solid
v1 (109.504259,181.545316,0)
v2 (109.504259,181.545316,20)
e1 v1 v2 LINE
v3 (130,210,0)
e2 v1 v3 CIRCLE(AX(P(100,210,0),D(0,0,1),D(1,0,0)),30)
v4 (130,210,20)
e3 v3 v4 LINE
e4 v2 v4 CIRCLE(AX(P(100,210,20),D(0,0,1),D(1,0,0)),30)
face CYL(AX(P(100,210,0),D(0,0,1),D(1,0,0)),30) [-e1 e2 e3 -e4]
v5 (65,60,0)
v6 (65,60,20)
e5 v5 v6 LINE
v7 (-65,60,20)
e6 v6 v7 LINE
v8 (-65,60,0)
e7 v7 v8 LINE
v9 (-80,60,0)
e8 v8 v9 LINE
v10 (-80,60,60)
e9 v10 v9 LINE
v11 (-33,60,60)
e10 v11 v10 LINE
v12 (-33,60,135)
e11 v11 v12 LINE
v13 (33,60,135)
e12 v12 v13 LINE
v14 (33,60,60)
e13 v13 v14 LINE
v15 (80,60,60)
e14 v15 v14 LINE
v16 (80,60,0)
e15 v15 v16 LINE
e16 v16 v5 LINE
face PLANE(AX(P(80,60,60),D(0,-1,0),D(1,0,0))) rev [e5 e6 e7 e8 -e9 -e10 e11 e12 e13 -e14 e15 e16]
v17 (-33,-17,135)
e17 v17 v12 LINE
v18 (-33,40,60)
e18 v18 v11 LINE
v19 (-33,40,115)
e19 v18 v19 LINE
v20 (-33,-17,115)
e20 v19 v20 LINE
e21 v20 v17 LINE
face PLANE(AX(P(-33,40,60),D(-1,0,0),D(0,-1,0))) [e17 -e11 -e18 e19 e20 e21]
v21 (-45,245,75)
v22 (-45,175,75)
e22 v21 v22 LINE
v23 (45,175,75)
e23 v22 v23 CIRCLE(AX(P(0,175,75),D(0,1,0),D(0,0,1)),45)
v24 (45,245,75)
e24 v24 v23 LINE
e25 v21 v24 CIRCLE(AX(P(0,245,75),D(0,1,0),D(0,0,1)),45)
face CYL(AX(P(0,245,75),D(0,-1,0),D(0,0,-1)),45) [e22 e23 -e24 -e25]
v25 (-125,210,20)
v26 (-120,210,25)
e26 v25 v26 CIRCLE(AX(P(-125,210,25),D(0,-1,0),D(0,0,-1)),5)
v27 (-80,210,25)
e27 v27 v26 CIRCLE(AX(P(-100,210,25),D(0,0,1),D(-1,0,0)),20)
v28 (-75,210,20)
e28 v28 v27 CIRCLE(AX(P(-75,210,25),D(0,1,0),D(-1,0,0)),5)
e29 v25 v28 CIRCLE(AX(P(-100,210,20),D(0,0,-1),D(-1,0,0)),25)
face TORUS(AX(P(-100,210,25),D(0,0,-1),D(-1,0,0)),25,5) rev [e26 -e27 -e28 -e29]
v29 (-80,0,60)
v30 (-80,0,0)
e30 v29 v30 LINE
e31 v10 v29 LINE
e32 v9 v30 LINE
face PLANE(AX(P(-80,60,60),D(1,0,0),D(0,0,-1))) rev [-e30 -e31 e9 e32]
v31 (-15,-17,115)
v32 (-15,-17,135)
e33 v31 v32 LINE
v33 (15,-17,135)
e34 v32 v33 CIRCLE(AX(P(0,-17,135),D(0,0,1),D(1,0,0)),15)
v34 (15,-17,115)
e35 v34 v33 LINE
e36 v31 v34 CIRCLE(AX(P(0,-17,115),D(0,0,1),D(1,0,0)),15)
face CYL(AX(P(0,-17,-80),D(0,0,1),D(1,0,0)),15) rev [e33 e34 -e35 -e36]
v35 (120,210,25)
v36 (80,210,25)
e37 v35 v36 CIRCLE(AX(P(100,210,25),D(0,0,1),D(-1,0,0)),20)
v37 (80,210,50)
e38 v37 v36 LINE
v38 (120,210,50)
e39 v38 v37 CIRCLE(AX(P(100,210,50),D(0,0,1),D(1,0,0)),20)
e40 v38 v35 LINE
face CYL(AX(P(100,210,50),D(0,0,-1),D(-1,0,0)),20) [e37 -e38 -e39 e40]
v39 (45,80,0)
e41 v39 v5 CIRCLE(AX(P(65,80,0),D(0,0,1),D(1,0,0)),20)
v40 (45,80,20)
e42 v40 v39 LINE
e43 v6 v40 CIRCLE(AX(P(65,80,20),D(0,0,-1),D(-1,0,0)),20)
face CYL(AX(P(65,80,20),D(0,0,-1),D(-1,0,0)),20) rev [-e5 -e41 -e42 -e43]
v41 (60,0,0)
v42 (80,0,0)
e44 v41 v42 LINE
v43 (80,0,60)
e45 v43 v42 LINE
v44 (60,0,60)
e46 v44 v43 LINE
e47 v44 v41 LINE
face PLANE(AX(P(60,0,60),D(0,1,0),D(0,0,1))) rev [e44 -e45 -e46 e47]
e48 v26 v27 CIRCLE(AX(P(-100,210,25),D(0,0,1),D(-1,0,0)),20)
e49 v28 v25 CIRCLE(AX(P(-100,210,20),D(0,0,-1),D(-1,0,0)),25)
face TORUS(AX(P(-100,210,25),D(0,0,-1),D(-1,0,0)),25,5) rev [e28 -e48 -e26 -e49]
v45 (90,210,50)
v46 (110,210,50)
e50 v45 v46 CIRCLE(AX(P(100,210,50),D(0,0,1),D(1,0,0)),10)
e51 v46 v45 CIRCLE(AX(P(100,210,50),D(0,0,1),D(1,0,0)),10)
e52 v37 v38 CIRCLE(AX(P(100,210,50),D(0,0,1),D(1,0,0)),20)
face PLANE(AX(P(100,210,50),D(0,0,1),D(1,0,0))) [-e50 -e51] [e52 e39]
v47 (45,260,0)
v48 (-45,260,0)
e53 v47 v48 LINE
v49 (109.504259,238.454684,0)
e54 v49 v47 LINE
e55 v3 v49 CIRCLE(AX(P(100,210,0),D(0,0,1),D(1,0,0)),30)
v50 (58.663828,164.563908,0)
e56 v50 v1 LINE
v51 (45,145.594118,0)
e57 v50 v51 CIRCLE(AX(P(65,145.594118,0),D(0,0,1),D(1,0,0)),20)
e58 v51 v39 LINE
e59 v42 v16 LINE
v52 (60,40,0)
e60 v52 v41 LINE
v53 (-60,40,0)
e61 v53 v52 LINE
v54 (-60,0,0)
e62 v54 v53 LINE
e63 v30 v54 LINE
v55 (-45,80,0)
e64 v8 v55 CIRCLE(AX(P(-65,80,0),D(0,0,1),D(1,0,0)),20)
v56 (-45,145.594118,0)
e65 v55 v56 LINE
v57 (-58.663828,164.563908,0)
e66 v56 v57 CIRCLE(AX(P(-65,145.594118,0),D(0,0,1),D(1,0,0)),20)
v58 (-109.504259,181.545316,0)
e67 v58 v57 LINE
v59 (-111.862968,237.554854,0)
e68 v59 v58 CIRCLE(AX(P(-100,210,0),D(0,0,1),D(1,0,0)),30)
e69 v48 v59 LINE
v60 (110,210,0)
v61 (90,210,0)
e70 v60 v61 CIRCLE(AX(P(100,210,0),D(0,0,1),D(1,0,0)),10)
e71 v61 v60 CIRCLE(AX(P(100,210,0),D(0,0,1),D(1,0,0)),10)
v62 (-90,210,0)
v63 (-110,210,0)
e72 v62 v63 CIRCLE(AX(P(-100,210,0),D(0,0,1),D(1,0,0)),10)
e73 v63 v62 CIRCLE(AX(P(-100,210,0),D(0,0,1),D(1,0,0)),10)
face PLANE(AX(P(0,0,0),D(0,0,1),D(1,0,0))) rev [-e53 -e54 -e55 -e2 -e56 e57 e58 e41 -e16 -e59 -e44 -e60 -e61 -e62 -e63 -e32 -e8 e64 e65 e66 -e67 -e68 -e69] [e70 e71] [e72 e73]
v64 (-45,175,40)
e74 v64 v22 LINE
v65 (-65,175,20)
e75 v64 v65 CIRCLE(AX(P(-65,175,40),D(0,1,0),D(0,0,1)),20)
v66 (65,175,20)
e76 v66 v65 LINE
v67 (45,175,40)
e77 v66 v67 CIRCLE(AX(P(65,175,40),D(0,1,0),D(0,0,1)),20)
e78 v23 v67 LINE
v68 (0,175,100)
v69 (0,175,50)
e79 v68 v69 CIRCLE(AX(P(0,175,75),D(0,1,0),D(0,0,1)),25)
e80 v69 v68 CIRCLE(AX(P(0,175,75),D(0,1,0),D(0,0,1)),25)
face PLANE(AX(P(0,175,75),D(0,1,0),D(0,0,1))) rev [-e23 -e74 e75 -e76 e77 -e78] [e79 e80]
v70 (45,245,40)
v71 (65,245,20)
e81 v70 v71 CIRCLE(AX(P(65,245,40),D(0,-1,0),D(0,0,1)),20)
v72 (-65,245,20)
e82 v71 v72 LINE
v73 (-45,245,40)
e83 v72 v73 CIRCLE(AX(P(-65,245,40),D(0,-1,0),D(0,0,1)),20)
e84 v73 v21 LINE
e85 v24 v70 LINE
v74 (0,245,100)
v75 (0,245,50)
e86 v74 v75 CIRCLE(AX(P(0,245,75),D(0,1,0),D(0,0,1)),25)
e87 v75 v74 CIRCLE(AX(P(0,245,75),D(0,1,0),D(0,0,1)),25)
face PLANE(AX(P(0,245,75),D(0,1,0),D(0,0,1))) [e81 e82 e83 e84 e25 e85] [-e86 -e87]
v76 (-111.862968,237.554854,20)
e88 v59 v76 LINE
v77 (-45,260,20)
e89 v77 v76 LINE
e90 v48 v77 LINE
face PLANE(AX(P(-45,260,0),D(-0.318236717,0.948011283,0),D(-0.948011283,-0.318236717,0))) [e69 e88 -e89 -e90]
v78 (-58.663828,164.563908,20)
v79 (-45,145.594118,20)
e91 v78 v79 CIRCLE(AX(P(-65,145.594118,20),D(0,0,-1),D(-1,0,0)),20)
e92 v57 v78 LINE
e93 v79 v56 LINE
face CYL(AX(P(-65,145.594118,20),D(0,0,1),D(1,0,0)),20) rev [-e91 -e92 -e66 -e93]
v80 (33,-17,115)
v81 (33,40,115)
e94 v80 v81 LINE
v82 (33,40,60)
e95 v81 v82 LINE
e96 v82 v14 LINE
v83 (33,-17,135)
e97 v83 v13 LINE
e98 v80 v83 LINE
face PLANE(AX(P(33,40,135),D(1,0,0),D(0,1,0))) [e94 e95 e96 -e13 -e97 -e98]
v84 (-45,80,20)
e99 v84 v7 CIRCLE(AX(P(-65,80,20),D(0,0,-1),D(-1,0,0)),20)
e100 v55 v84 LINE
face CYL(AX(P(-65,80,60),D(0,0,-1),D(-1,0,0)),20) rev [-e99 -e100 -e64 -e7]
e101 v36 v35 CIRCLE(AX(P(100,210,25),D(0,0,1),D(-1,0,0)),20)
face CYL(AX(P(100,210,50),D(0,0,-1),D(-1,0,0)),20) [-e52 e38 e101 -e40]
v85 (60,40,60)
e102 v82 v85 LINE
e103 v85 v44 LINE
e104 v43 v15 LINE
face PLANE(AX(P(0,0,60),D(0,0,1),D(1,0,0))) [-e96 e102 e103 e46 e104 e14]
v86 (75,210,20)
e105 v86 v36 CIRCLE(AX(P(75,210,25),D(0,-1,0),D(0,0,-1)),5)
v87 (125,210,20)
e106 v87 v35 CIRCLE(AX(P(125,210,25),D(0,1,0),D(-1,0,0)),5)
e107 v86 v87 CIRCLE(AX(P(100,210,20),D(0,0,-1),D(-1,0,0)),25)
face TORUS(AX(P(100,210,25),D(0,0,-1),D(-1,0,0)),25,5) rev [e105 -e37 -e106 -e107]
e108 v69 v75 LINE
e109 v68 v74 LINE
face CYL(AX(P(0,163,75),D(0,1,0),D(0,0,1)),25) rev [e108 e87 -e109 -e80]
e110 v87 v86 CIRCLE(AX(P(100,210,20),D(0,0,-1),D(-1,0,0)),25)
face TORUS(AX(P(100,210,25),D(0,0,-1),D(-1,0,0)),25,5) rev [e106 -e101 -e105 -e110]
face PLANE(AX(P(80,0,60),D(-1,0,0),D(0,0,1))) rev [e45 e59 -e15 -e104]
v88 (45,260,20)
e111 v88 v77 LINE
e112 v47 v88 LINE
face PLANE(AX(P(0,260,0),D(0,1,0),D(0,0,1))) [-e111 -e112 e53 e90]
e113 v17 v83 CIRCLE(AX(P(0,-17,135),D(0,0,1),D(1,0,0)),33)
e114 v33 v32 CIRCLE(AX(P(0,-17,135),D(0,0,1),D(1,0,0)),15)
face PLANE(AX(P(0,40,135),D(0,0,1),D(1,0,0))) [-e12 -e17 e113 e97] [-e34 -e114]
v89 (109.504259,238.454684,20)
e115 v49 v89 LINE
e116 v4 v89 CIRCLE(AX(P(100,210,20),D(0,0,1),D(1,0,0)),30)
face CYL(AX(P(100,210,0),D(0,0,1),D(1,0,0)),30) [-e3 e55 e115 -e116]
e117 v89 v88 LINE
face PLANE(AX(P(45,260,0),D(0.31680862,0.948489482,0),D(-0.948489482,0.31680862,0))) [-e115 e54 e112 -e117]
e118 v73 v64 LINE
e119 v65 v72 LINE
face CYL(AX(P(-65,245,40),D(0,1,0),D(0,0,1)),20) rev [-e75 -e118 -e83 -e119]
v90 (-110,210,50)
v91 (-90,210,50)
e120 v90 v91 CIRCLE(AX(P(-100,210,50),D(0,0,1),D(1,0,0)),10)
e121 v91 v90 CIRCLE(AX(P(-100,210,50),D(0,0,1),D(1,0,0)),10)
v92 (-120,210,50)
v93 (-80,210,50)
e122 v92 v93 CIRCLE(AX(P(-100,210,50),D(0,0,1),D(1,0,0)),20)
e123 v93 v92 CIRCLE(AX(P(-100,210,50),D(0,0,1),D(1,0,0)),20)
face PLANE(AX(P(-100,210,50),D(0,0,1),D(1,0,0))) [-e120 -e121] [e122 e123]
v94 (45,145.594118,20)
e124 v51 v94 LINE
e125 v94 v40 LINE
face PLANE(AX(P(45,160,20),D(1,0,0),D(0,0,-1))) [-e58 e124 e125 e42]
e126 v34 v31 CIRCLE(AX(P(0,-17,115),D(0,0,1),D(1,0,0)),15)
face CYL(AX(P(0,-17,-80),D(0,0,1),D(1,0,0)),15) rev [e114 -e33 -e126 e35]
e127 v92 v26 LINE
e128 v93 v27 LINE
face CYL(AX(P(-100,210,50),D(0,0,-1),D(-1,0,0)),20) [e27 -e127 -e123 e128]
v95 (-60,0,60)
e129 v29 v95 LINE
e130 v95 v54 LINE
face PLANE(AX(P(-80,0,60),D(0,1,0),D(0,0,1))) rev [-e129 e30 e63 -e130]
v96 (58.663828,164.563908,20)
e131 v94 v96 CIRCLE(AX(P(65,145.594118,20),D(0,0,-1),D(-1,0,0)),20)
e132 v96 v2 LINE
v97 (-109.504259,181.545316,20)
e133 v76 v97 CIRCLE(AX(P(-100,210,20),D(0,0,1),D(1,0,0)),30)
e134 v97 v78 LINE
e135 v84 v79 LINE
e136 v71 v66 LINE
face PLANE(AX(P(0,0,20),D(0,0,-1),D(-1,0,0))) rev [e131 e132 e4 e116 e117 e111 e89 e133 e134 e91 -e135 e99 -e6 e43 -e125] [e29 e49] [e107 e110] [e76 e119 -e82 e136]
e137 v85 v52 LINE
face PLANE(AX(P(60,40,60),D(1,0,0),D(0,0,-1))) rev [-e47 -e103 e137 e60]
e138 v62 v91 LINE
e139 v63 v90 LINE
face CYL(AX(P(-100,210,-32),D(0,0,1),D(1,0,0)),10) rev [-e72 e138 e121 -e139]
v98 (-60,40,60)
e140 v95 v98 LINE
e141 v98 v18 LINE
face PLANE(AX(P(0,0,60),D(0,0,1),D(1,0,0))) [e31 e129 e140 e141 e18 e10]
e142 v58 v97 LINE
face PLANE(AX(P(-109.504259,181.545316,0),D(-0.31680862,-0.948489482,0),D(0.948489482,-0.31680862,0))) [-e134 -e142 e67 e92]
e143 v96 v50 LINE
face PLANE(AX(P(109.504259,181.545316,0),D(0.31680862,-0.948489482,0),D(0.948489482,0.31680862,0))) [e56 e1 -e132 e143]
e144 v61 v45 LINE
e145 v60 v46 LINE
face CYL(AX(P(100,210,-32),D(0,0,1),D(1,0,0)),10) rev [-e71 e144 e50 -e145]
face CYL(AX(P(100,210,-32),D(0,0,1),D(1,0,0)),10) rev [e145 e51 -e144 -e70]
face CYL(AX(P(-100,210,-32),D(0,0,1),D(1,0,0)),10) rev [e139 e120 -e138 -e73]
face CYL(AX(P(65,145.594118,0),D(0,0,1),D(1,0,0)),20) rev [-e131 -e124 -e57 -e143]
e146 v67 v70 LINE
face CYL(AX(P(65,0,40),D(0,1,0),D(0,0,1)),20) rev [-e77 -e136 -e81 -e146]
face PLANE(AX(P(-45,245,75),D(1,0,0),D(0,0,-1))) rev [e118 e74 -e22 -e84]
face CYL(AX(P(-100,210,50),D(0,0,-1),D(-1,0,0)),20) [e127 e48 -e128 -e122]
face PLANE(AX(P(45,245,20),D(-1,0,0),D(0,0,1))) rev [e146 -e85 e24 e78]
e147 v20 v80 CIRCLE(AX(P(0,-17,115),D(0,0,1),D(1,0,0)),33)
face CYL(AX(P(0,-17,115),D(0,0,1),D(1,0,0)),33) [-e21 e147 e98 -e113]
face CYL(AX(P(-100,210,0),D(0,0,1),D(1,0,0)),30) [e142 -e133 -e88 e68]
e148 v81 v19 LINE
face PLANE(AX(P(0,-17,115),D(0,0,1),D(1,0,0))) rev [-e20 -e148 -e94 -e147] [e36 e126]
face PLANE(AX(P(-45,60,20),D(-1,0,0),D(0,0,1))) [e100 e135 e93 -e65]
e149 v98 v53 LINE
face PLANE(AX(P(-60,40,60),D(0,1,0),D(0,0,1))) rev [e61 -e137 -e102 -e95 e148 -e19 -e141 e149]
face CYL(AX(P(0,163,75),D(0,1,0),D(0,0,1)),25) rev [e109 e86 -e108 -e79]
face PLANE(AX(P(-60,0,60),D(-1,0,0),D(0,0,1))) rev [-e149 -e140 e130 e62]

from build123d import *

# Parameters (mm, degrees)
BASE_BLOCK_DEPTH               = 60
CLEVIS_LUG_DEPTH               = 20
LUG_EXTENSION_DEPTH            = 20
PIN_HOLE_SKETCH_30_R           = 15
CLEVIS_PIN_HOLE_30_DEPTH       = 215
UPRIGHT_WEB_DEPTH              = 20
FLANGE_PLATE_DEPTH             = 20
WEB_FLANGE_FILLET_R20_A_R      = 20
WEB_FLANGE_FILLET_R20_B_R      = 20
WEB_BASE_FILLET_R20_A_R        = 20
WEB_BASE_FILLET_R20_B_R        = 20
HUB_BOSS_DEPTH                 = 35
HUB_WEB_FILLET_R20_A_R         = 20
HUB_WEB_FILLET_R20_B_R         = 20
MOUNTING_BOSSES_SKETCH_2X_40_R = 20
MOUNTING_BOSSES_2X_40_DEPTH    = 30
MOUNTING_BOSS_FILLET_R5_A_R    = 5
MOUNTING_BOSS_FILLET_R5_B_R    = 5
HUB_BORE_SKETCH_50_R           = 25
HUB_BORE_50_DEPTH              = 82
MOUNTING_HOLES_SKETCH_2X_20_R  = 10
MOUNTING_HOLES_2X_20_DEPTH     = 82


with BuildPart() as part:
    # Base Profile Sketch → Base Block (new body)
    with BuildSketch(Plane.XY):
        Polygon((60, 0), (80, 0), (80, 60), (-80, 60), (-80, 0), (-60, 0), (-60, 40), (60, 40), align=None)
    extrude(amount=BASE_BLOCK_DEPTH)

    # Clevis Lug Sketch → Clevis Lug (add)
    with BuildSketch(Plane(origin=(0, 60, 0), x_dir=(1, 0, 0), z_dir=(0, 1, 0))):
        Polygon((0, -135), (33, -135), (33, -60), (-33, -60), (-33, -135), align=None)
    extrude(amount=-CLEVIS_LUG_DEPTH)

    # Lug Extension Sketch → Lug Extension (add)
    with BuildSketch(Plane.XY.offset(135)):
        with BuildLine():
            Line((33, -17), (33, 40))
            Line((33, 40), (-33, 40))
            Line((-33, 40), (-33, -17))
            ThreePointArc((-33, -17), (0, -50), (33, -17))
        make_face()
    extrude(amount=-LUG_EXTENSION_DEPTH)

    # Pin Hole Sketch Ø30 → Clevis Pin Hole Ø30 (cut)
    with BuildSketch(Plane.XY.offset(135)):
        with Locations((0, -17)):
            Circle(PIN_HOLE_SKETCH_30_R)
    extrude(amount=-CLEVIS_PIN_HOLE_30_DEPTH, mode=Mode.SUBTRACT)

    # Upright Web Sketch → Upright Web (add)
    with BuildSketch(Plane(origin=(0, 0, 0), x_dir=(-1, 0, 0), z_dir=(0, 0, -1))):
        Polygon((0, 60), (45, 60), (45, 160), (-45, 160), (-45, 60), align=None)
    extrude(amount=-UPRIGHT_WEB_DEPTH)

    # Flange Plate Sketch → Flange Plate (add)
    with BuildSketch(Plane.XY.offset(20)):
        with BuildLine():
            Line((0, 260), (45, 260))
            Line((45, 260), (109.504258609, 238.45468447))
            ThreePointArc((109.504258609, 238.45468447), (130, 210), (109.504258609, 181.54531553))
            Line((109.504258609, 181.54531553), (45, 160))
            Line((45, 160), (-45, 160))
            Line((-45, 160), (-109.504258609, 181.54531553))
            ThreePointArc((-109.504258609, 181.54531553), (-129.973433228, 208.737739921), (-111.86296755, 237.554854398))
            Line((-111.86296755, 237.554854398), (-45, 260))
            Line((-45, 260), (0, 260))
        make_face()
    extrude(amount=-FLANGE_PLATE_DEPTH)

    # Web-Flange Fillet R20 A
    web_flange_fillet_r20_a_edges = [part.edges().sort_by_distance(p)[0] for p in [
        (-45, 160, 10),
    ]]
    fillet(web_flange_fillet_r20_a_edges, radius=WEB_FLANGE_FILLET_R20_A_R)

    # Web-Flange Fillet R20 B
    web_flange_fillet_r20_b_edges = [part.edges().sort_by_distance(p)[0] for p in [
        (45, 160, 10),
    ]]
    fillet(web_flange_fillet_r20_b_edges, radius=WEB_FLANGE_FILLET_R20_B_R)

    # Web-Base Fillet R20 A
    web_base_fillet_r20_a_edges = [part.edges().sort_by_distance(p)[0] for p in [
        (45, 60, 10),
    ]]
    fillet(web_base_fillet_r20_a_edges, radius=WEB_BASE_FILLET_R20_A_R)

    # Web-Base Fillet R20 B
    web_base_fillet_r20_b_edges = [part.edges().sort_by_distance(p)[0] for p in [
        (-45, 60, 10),
    ]]
    fillet(web_base_fillet_r20_b_edges, radius=WEB_BASE_FILLET_R20_B_R)

    # Hub Sketch → Hub Boss (add, symmetric)
    with BuildSketch(Plane(origin=(0, 210, 0), x_dir=(1, 0, 0), z_dir=(0, 1, 0))):
        with BuildLine():
            Line((-45, -75), (-45, -20))
            Line((-45, -20), (45, -20))
            Line((45, -20), (45, -75))
            ThreePointArc((45, -75), (0, -120), (-45, -75))
        make_face()
    extrude(amount=HUB_BOSS_DEPTH, both=True)

    # Hub-Web Fillet R20 A
    hub_web_fillet_r20_a_edges = [part.edges().sort_by_distance(p)[0] for p in [
        (-45, 210, 20),
    ]]
    fillet(hub_web_fillet_r20_a_edges, radius=HUB_WEB_FILLET_R20_A_R)

    # Hub-Web Fillet R20 B
    hub_web_fillet_r20_b_edges = [part.edges().sort_by_distance(p)[0] for p in [
        (45, 210, 20),
    ]]
    fillet(hub_web_fillet_r20_b_edges, radius=HUB_WEB_FILLET_R20_B_R)

    # Mounting Bosses Sketch 2xØ40 → Mounting Bosses 2xØ40 (add)
    with BuildSketch(Plane.XY.offset(20)):
        with Locations(Location((100, 210, 0), (0, 0, 180))):
            Circle(MOUNTING_BOSSES_SKETCH_2X_40_R)
        with Locations(Location((-100, 210, 0), (0, 0, 180))):
            Circle(MOUNTING_BOSSES_SKETCH_2X_40_R)
    extrude(amount=MOUNTING_BOSSES_2X_40_DEPTH)

    # Mounting Boss Fillet R5 A
    mounting_boss_fillet_r5_a_edges = [part.edges().sort_by_distance(p)[0] for p in [
        (120, 210, 20),
    ]]
    fillet(mounting_boss_fillet_r5_a_edges, radius=MOUNTING_BOSS_FILLET_R5_A_R)

    # Mounting Boss Fillet R5 B
    mounting_boss_fillet_r5_b_edges = [part.edges().sort_by_distance(p)[0] for p in [
        (-80, 210, 20),
    ]]
    fillet(mounting_boss_fillet_r5_b_edges, radius=MOUNTING_BOSS_FILLET_R5_B_R)

    # Hub Bore Sketch Ø50 → Hub Bore Ø50 (cut)
    with BuildSketch(Plane(origin=(0, 245, 0), x_dir=(1, 0, 0), z_dir=(0, 1, 0))):
        with Locations(Location((0, -75, 0), (0, 0, 270))):
            Circle(HUB_BORE_SKETCH_50_R)
    extrude(amount=-HUB_BORE_50_DEPTH, mode=Mode.SUBTRACT)

    # Mounting Holes Sketch 2xØ20 → Mounting Holes 2xØ20 (cut)
    with BuildSketch(Plane.XY.offset(50)):
        with Locations((100, 210)):
            Circle(MOUNTING_HOLES_SKETCH_2X_20_R)
        with Locations((-100, 210)):
            Circle(MOUNTING_HOLES_SKETCH_2X_20_R)
    extrude(amount=-MOUNTING_HOLES_2X_20_DEPTH, mode=Mode.SUBTRACT)


solid = part.part
